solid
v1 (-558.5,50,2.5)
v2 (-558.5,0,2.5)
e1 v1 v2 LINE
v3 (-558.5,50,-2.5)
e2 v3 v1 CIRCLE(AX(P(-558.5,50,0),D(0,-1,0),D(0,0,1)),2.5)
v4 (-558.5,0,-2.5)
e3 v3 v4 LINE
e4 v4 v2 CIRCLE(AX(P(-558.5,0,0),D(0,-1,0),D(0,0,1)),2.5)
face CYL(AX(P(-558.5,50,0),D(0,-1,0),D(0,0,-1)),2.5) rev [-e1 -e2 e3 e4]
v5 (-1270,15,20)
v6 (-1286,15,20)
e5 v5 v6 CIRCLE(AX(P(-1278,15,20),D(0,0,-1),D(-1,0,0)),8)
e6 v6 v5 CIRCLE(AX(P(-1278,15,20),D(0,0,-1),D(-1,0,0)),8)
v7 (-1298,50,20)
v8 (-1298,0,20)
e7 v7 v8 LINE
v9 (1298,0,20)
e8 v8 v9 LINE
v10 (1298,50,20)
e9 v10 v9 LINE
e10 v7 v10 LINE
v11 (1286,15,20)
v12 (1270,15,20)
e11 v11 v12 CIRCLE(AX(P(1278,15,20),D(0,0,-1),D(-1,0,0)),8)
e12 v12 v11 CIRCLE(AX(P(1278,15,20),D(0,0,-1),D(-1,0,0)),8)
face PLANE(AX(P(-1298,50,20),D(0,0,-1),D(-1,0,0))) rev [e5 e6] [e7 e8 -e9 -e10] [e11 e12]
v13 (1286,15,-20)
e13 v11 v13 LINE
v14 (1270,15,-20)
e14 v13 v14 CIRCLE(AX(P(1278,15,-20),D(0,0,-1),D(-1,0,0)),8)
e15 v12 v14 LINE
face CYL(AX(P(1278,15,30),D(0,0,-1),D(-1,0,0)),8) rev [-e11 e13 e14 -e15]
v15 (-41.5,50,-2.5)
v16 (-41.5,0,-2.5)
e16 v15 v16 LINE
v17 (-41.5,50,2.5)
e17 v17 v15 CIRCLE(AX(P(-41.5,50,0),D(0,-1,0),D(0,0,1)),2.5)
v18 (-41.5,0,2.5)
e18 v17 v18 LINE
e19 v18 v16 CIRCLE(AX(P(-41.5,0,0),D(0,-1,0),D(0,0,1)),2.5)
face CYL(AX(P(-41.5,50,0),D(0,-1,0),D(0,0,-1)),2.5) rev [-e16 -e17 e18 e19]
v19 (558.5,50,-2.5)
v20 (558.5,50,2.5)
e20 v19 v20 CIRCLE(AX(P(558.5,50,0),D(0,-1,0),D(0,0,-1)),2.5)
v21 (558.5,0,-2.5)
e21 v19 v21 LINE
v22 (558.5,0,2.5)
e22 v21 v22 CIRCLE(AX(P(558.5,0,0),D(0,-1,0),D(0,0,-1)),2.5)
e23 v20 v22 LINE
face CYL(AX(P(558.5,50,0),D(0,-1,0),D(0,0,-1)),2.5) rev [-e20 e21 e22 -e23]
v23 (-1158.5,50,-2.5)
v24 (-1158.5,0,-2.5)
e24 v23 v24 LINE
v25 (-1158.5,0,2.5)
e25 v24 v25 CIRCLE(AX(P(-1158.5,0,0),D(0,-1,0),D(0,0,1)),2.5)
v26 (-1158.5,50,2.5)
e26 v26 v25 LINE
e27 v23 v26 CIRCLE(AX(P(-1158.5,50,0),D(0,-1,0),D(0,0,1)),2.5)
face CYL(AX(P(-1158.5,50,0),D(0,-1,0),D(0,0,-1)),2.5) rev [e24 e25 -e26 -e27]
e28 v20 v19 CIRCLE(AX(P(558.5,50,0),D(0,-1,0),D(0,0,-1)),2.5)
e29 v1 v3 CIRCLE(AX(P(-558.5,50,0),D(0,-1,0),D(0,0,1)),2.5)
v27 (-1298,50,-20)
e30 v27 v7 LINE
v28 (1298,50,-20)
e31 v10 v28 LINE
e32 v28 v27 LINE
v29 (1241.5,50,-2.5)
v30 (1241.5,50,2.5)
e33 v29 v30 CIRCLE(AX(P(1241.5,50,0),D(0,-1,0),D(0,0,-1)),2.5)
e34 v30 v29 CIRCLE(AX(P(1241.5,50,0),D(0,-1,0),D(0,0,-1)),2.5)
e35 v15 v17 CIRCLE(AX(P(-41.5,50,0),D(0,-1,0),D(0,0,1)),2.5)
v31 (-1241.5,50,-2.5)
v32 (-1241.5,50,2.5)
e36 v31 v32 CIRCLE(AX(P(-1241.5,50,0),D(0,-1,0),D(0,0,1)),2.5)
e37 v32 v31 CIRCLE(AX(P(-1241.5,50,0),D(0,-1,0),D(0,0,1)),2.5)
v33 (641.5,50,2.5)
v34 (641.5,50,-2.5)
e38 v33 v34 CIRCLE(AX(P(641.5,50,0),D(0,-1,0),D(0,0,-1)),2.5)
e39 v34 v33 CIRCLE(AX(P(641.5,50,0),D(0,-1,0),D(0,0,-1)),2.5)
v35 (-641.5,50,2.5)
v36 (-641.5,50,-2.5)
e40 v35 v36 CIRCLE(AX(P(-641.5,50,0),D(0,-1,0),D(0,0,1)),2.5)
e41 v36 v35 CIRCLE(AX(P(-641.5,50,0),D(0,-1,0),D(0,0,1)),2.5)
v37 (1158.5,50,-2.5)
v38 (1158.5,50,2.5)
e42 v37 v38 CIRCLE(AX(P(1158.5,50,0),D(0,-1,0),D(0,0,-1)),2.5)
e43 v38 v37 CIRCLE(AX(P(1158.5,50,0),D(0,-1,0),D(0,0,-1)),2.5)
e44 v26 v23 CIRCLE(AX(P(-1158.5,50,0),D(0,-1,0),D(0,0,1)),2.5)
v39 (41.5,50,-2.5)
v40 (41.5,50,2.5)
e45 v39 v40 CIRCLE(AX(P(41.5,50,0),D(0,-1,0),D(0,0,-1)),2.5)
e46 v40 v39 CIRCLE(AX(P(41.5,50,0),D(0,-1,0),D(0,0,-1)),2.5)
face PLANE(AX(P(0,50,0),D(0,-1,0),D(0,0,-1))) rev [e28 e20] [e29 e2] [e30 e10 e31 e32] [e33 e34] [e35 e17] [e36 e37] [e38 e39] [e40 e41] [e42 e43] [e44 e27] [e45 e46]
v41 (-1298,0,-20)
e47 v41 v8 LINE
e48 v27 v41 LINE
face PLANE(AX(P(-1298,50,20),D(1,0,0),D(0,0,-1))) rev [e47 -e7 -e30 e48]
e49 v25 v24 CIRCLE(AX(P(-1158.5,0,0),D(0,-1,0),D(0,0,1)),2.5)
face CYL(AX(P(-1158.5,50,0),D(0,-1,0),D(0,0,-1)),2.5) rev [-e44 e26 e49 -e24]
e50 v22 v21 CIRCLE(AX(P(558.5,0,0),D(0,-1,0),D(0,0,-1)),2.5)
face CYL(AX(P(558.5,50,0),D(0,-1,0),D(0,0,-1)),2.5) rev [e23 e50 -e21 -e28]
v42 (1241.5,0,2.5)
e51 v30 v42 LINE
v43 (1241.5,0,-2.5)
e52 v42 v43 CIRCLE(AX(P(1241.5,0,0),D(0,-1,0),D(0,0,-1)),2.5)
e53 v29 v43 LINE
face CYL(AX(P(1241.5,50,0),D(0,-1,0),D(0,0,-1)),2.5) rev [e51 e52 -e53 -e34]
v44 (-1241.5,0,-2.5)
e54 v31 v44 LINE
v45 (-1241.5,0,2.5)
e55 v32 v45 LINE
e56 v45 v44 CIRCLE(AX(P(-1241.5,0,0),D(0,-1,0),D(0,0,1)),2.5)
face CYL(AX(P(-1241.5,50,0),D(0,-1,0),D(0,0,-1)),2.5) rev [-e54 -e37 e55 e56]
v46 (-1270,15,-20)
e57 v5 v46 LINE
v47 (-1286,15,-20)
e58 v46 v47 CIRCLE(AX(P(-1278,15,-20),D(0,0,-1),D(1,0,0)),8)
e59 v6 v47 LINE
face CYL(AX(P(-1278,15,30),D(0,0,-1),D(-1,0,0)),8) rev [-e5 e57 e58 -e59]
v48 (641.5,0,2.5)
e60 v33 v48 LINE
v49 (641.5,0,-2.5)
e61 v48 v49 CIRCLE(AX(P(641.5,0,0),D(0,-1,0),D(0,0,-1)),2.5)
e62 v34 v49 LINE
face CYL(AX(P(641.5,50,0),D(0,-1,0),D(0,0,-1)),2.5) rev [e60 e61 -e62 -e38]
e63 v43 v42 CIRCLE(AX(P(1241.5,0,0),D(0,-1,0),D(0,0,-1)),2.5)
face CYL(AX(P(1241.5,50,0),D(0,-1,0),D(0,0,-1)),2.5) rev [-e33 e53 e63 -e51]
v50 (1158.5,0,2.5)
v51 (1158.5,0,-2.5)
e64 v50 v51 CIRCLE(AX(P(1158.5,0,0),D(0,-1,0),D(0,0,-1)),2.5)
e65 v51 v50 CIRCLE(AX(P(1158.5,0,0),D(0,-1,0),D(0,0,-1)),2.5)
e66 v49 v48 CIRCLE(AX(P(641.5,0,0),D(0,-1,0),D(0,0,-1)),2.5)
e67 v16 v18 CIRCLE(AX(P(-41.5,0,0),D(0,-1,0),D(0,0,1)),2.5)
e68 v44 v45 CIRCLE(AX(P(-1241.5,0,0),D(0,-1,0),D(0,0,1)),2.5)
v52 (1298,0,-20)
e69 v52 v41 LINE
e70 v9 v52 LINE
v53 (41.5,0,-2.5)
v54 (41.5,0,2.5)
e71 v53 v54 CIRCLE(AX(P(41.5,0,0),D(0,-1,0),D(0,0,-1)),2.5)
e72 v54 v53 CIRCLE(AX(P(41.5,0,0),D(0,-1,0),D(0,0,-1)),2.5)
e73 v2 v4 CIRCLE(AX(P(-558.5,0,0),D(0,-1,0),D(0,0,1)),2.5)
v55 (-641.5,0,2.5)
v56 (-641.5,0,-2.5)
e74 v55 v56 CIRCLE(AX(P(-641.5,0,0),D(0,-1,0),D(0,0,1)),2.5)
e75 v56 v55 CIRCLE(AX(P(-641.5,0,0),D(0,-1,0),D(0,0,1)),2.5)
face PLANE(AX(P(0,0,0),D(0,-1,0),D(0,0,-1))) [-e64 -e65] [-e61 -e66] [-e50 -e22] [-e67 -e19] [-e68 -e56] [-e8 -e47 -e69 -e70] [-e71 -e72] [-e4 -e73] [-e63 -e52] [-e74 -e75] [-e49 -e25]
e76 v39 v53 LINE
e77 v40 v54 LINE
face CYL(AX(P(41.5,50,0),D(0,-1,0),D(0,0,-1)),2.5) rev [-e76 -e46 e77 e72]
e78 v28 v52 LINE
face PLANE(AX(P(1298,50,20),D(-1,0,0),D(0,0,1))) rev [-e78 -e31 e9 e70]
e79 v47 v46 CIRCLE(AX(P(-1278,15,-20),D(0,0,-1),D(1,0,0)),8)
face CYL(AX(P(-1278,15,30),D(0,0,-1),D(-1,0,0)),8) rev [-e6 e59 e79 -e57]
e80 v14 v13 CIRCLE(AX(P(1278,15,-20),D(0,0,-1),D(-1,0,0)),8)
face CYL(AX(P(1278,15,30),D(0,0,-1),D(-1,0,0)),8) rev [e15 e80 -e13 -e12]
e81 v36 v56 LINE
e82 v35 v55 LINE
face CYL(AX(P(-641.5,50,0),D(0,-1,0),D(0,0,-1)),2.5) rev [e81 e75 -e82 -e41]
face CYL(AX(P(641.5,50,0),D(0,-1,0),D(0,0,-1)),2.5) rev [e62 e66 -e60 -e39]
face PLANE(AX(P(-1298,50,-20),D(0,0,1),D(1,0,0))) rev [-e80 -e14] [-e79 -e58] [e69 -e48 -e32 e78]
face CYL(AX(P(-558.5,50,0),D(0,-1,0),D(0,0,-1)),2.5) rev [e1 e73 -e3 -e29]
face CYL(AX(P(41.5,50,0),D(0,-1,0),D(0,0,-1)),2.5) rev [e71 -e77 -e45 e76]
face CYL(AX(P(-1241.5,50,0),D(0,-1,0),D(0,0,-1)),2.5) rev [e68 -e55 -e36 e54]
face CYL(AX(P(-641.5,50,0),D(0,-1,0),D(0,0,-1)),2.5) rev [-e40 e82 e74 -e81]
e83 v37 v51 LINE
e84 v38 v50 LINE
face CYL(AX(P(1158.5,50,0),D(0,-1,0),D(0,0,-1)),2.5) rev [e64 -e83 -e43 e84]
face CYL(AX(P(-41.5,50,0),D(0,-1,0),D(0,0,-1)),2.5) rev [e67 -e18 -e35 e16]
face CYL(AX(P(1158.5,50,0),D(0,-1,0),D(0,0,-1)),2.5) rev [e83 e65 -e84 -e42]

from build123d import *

# Parameters (mm, degrees)
SKETCH1_W           = 2596
SKETCH1_H           = 40
BOSS_EXTRUDE1_DEPTH = 50
SKETCH2_R           = 2.5
CUT_EXTRUDE1_DEPTH  = 50
SKETCH3_R           = 8
CUT_EXTRUDE2_DEPTH  = 50


with BuildPart() as part:
    # Sketch1 → Boss-Extrude1 (new body)
    with BuildSketch(Plane(origin=(0, 0, 0), x_dir=(1, 0, 0), z_dir=(0, 1, 0))):
        Rectangle(SKETCH1_W, SKETCH1_H)
    extrude(amount=BOSS_EXTRUDE1_DEPTH)

    # Sketch2 → Cut-Extrude1 (cut)
    with BuildSketch(Plane.XZ):
        with Locations(Location((1241.5, 0, 0), (0, 0, 270))):
            Circle(SKETCH2_R)
        with Locations(Location((1158.5, 0, 0), (0, 0, 270))):
            Circle(SKETCH2_R)
        with Locations(Location((641.5, 0, 0), (0, 0, 270))):
            Circle(SKETCH2_R)
        with Locations(Location((558.5, 0, 0), (0, 0, 270))):
            Circle(SKETCH2_R)
        with Locations(Location((41.5, 0, 0), (0, 0, 270))):
            Circle(SKETCH2_R)
        with Locations(Location((-41.5, 0, 0), (0, 0, 90))):
            Circle(SKETCH2_R)
        with Locations(Location((-558.5, 0, 0), (0, 0, 90))):
            Circle(SKETCH2_R)
        with Locations(Location((-641.5, 0, 0), (0, 0, 90))):
            Circle(SKETCH2_R)
        with Locations(Location((-1158.5, 0, 0), (0, 0, 90))):
            Circle(SKETCH2_R)
        with Locations(Location((-1241.5, 0, 0), (0, 0, 90))):
            Circle(SKETCH2_R)
    extrude(amount=-CUT_EXTRUDE1_DEPTH, mode=Mode.SUBTRACT)

    # Sketch3 → Cut-Extrude2 (cut)
    with BuildSketch(Plane(origin=(0, 0, -20), x_dir=(-1, 0, 0), z_dir=(0, 0, -1))):
        with Locations((-1278, 15)):
            Circle(SKETCH3_R)
        with Locations((1278, 15)):
            Circle(SKETCH3_R)
    extrude(amount=-CUT_EXTRUDE2_DEPTH, mode=Mode.SUBTRACT)


solid = part.part
